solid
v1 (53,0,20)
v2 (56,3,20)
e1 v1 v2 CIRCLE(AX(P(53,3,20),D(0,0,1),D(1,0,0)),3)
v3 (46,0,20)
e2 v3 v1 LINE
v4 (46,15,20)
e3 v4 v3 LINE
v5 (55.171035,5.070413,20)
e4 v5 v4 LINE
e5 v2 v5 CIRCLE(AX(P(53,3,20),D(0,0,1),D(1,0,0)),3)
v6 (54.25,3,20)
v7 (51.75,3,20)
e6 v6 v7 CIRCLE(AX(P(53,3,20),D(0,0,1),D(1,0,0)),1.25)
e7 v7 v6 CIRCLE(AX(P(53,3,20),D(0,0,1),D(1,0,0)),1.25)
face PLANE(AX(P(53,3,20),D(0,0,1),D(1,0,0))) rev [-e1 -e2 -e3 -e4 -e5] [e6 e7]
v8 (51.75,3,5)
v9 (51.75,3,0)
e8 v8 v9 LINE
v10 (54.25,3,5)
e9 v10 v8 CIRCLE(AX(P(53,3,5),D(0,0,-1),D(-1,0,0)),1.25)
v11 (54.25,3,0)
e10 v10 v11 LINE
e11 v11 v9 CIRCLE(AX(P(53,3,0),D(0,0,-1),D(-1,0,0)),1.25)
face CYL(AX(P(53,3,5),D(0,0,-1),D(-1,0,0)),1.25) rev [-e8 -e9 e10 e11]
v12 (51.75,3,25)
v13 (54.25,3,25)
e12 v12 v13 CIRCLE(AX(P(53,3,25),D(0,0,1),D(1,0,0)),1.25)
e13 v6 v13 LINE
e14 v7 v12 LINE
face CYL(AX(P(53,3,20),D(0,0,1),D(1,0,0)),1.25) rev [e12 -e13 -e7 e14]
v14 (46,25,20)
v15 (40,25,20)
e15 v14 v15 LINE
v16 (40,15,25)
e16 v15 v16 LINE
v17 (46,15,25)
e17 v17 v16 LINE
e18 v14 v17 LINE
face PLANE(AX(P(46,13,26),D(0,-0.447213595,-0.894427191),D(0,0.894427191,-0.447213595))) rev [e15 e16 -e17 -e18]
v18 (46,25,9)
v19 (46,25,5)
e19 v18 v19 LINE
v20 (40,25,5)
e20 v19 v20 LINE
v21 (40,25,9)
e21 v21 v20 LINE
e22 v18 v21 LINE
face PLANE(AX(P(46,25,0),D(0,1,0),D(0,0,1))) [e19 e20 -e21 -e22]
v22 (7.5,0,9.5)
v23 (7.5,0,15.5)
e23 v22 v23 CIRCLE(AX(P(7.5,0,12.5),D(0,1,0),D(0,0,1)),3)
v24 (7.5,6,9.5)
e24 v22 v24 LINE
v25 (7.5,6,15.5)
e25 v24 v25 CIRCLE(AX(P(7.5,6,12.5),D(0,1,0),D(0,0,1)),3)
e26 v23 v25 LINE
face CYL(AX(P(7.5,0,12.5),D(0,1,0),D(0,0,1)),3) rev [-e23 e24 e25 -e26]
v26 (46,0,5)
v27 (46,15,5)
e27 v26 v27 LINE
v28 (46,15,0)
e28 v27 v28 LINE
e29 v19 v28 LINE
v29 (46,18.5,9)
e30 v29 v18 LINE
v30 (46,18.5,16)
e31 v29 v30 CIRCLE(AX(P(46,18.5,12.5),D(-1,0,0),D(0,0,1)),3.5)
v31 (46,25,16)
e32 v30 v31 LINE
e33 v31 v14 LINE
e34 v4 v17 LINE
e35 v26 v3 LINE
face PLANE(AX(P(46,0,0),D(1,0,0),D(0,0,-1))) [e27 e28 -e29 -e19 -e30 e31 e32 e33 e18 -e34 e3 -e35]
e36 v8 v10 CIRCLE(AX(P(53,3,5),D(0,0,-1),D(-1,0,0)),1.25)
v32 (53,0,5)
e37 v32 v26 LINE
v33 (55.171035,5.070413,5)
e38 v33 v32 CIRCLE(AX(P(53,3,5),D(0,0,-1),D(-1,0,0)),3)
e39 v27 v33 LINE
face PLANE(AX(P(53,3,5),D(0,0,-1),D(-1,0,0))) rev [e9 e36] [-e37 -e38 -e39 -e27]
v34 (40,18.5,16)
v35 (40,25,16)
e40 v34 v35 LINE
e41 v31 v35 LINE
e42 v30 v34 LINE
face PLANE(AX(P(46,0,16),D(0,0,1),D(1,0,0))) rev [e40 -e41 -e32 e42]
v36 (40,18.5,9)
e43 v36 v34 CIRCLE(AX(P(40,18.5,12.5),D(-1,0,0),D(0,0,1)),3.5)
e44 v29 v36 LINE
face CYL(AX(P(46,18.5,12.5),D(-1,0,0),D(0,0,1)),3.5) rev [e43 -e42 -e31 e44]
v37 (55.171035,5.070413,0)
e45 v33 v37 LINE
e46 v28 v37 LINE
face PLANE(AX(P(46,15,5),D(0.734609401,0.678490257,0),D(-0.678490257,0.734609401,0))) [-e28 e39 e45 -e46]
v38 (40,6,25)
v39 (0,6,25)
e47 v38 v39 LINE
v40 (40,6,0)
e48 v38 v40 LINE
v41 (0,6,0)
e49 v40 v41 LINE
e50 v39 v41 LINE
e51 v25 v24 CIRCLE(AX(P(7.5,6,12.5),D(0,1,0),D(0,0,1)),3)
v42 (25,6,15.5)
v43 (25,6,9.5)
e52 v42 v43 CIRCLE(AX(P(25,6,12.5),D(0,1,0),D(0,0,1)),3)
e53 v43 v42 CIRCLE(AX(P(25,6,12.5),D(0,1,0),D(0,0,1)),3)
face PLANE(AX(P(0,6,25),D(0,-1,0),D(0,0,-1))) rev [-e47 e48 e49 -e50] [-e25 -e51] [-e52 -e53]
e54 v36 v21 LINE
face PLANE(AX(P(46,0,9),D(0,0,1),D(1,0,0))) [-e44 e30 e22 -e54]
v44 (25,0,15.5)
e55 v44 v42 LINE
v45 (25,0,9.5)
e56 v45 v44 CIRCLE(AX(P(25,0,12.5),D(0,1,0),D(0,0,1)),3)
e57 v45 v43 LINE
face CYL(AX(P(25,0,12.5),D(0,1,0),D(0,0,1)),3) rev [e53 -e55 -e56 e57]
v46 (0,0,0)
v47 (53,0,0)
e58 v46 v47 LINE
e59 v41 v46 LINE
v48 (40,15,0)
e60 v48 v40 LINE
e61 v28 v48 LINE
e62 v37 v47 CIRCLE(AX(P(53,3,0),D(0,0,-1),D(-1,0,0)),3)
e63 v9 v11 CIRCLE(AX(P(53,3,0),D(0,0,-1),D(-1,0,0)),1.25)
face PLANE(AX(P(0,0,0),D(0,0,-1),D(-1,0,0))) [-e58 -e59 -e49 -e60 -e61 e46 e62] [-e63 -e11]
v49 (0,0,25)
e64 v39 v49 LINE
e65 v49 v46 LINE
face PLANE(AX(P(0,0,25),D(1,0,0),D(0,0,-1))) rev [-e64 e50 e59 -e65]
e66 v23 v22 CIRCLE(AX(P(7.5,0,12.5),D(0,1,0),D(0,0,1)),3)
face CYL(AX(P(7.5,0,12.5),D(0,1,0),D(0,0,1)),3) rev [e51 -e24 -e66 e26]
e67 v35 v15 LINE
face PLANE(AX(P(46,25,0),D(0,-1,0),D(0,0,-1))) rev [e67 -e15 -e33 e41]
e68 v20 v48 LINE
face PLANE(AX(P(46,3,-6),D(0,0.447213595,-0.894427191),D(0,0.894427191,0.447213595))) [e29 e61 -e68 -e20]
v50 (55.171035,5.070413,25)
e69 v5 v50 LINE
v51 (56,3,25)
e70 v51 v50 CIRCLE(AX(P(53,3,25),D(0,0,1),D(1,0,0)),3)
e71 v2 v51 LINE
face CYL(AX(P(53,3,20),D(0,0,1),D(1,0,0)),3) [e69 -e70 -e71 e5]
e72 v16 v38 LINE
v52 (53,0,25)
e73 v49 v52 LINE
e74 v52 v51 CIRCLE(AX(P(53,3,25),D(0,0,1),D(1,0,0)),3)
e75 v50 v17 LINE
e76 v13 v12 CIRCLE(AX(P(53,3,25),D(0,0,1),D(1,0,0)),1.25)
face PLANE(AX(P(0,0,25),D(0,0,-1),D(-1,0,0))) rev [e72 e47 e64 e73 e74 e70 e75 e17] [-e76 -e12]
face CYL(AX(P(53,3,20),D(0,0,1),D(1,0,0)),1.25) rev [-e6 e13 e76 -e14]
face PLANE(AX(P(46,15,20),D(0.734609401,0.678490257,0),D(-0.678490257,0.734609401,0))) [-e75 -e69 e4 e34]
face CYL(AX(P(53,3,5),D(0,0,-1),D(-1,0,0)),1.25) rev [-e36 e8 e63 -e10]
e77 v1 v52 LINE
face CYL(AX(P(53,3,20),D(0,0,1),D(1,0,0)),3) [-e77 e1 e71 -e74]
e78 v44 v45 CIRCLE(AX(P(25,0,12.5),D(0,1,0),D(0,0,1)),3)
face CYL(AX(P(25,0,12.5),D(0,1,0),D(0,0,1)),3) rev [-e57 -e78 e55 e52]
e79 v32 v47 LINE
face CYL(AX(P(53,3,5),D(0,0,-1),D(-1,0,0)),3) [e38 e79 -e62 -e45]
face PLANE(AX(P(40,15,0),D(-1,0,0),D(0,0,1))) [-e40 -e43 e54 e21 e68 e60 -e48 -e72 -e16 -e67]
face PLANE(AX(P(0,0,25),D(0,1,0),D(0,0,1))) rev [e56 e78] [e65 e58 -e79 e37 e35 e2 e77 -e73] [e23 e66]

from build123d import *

# Parameters (mm, degrees)
BASE_PROFILE_SKETCH_W      = 40
BASE_PROFILE_SKETCH_H      = 6
BASE_BODY_DEPTH            = 25
UPRIGHT_BLOCK_SKETCH_W     = 6
UPRIGHT_BLOCK_SKETCH_H     = 15
UPRIGHT_BLOCK_DEPTH        = 25
SLOTTED_CLEVIS_PLATE_DEPTH = 6
LUG_1_DEPTH                = 5
LUG_1_PIN_HOLE_SKETCH_R    = 1.25
LUG_1_PIN_HOLE_DEPTH       = 5
LUG_START                  = -5
LUG_2_DEPTH                = 5
LUG_2_PIN_HOLE_SKETCH_R    = 1.25
LUG_2_PIN_HOLE_DEPTH       = 5
MOUNTING_HOLES_SKETCH_R    = 3
MOUNTING_HOLES_2X_6_DEPTH  = 6


with BuildPart() as part:
    # Base Profile Sketch → Base Body (new body)
    with BuildSketch(Plane.XY):
        with Locations((20, 3)):
            Rectangle(BASE_PROFILE_SKETCH_W, BASE_PROFILE_SKETCH_H)
    extrude(amount=BASE_BODY_DEPTH)

    # Upright Block Sketch → Upright Block (add)
    with BuildSketch(Plane.XY.offset(25)):
        with Locations((43, 7.5)):
            Rectangle(UPRIGHT_BLOCK_SKETCH_W, UPRIGHT_BLOCK_SKETCH_H)
    extrude(amount=-UPRIGHT_BLOCK_DEPTH)

    # Clevis Slot Profile Sketch → Slotted Clevis Plate (add)
    with BuildSketch(Plane.ZY.offset(-40)):
        with BuildLine():
            ThreePointArc((16, 18.5), (14.974873734, 16.025126266), (12.5, 15))
            Line((12.5, 15), (25, 15))
            Line((25, 15), (20, 25))
            Line((20, 25), (16, 25))
            Line((16, 25), (16, 18.5))
        make_face()
        with BuildLine():
            ThreePointArc((12.5, 15), (10.025126266, 16.025126266), (9, 18.5))
            Line((9, 18.5), (9, 25))
            Line((9, 25), (5, 25))
            Line((5, 25), (0, 15))
            Line((0, 15), (12.5, 15))
        make_face()
    extrude(amount=-SLOTTED_CLEVIS_PLATE_DEPTH)

    # Lug 1 Sketch → Lug 1 (add)
    with BuildSketch(Plane.XY.offset(25)):
        with BuildLine():
            Line((46, 0), (53, 0))
            ThreePointArc((53, 0), (55.757828687, 1.81916092), (55.171034593, 5.070412712))
            Line((55.171034593, 5.070412712), (46, 15))
            Line((46, 15), (46, 0))
        make_face()
    extrude(amount=-LUG_1_DEPTH)

    # Lug 1 Pin Hole Sketch → Lug 1 Pin Hole (cut)
    with BuildSketch(Plane.XY.offset(25)):
        with Locations((53, 3)):
            Circle(LUG_1_PIN_HOLE_SKETCH_R)
    extrude(amount=-LUG_1_PIN_HOLE_DEPTH, mode=Mode.SUBTRACT)

    # Lug 2 Sketch → Lug 2 (add)
    with BuildSketch(Plane(origin=(0, 0, 0), x_dir=(-1, 0, 0), z_dir=(0, 0, -1)).offset(LUG_START)):
        with BuildLine():
            Line((-46, 0), (-53, 0))
            ThreePointArc((-53, 0), (-55.757828687, 1.81916092), (-55.171034593, 5.070412712))
            Line((-55.171034593, 5.070412712), (-46, 15))
            Line((-46, 15), (-46, 0))
        make_face()
    extrude(amount=LUG_2_DEPTH)

    # Lug 2 Pin Hole Sketch → Lug 2 Pin Hole (cut)
    with BuildSketch(Plane(origin=(0, 0, 0), x_dir=(-1, 0, 0), z_dir=(0, 0, -1)).offset(LUG_START)):
        with Locations(Location((-53, 3, 0), (0, 0, 180))):
            Circle(LUG_2_PIN_HOLE_SKETCH_R)
    extrude(amount=LUG_2_PIN_HOLE_DEPTH, mode=Mode.SUBTRACT)

    # Mounting Holes Sketch → Mounting Holes 2xØ6 (cut)
    with BuildSketch(Plane(origin=(0, 6, 0), x_dir=(1, 0, 0), z_dir=(0, 1, 0))):
        with Locations(Location((7.5, -12.5, 0), (0, 0, 270))):
            Circle(MOUNTING_HOLES_SKETCH_R)
        with Locations(Location((25, -12.5, 0), (0, 0, 270))):
            Circle(MOUNTING_HOLES_SKETCH_R)
    extrude(amount=-MOUNTING_HOLES_2X_6_DEPTH, mode=Mode.SUBTRACT)


solid = part.part
